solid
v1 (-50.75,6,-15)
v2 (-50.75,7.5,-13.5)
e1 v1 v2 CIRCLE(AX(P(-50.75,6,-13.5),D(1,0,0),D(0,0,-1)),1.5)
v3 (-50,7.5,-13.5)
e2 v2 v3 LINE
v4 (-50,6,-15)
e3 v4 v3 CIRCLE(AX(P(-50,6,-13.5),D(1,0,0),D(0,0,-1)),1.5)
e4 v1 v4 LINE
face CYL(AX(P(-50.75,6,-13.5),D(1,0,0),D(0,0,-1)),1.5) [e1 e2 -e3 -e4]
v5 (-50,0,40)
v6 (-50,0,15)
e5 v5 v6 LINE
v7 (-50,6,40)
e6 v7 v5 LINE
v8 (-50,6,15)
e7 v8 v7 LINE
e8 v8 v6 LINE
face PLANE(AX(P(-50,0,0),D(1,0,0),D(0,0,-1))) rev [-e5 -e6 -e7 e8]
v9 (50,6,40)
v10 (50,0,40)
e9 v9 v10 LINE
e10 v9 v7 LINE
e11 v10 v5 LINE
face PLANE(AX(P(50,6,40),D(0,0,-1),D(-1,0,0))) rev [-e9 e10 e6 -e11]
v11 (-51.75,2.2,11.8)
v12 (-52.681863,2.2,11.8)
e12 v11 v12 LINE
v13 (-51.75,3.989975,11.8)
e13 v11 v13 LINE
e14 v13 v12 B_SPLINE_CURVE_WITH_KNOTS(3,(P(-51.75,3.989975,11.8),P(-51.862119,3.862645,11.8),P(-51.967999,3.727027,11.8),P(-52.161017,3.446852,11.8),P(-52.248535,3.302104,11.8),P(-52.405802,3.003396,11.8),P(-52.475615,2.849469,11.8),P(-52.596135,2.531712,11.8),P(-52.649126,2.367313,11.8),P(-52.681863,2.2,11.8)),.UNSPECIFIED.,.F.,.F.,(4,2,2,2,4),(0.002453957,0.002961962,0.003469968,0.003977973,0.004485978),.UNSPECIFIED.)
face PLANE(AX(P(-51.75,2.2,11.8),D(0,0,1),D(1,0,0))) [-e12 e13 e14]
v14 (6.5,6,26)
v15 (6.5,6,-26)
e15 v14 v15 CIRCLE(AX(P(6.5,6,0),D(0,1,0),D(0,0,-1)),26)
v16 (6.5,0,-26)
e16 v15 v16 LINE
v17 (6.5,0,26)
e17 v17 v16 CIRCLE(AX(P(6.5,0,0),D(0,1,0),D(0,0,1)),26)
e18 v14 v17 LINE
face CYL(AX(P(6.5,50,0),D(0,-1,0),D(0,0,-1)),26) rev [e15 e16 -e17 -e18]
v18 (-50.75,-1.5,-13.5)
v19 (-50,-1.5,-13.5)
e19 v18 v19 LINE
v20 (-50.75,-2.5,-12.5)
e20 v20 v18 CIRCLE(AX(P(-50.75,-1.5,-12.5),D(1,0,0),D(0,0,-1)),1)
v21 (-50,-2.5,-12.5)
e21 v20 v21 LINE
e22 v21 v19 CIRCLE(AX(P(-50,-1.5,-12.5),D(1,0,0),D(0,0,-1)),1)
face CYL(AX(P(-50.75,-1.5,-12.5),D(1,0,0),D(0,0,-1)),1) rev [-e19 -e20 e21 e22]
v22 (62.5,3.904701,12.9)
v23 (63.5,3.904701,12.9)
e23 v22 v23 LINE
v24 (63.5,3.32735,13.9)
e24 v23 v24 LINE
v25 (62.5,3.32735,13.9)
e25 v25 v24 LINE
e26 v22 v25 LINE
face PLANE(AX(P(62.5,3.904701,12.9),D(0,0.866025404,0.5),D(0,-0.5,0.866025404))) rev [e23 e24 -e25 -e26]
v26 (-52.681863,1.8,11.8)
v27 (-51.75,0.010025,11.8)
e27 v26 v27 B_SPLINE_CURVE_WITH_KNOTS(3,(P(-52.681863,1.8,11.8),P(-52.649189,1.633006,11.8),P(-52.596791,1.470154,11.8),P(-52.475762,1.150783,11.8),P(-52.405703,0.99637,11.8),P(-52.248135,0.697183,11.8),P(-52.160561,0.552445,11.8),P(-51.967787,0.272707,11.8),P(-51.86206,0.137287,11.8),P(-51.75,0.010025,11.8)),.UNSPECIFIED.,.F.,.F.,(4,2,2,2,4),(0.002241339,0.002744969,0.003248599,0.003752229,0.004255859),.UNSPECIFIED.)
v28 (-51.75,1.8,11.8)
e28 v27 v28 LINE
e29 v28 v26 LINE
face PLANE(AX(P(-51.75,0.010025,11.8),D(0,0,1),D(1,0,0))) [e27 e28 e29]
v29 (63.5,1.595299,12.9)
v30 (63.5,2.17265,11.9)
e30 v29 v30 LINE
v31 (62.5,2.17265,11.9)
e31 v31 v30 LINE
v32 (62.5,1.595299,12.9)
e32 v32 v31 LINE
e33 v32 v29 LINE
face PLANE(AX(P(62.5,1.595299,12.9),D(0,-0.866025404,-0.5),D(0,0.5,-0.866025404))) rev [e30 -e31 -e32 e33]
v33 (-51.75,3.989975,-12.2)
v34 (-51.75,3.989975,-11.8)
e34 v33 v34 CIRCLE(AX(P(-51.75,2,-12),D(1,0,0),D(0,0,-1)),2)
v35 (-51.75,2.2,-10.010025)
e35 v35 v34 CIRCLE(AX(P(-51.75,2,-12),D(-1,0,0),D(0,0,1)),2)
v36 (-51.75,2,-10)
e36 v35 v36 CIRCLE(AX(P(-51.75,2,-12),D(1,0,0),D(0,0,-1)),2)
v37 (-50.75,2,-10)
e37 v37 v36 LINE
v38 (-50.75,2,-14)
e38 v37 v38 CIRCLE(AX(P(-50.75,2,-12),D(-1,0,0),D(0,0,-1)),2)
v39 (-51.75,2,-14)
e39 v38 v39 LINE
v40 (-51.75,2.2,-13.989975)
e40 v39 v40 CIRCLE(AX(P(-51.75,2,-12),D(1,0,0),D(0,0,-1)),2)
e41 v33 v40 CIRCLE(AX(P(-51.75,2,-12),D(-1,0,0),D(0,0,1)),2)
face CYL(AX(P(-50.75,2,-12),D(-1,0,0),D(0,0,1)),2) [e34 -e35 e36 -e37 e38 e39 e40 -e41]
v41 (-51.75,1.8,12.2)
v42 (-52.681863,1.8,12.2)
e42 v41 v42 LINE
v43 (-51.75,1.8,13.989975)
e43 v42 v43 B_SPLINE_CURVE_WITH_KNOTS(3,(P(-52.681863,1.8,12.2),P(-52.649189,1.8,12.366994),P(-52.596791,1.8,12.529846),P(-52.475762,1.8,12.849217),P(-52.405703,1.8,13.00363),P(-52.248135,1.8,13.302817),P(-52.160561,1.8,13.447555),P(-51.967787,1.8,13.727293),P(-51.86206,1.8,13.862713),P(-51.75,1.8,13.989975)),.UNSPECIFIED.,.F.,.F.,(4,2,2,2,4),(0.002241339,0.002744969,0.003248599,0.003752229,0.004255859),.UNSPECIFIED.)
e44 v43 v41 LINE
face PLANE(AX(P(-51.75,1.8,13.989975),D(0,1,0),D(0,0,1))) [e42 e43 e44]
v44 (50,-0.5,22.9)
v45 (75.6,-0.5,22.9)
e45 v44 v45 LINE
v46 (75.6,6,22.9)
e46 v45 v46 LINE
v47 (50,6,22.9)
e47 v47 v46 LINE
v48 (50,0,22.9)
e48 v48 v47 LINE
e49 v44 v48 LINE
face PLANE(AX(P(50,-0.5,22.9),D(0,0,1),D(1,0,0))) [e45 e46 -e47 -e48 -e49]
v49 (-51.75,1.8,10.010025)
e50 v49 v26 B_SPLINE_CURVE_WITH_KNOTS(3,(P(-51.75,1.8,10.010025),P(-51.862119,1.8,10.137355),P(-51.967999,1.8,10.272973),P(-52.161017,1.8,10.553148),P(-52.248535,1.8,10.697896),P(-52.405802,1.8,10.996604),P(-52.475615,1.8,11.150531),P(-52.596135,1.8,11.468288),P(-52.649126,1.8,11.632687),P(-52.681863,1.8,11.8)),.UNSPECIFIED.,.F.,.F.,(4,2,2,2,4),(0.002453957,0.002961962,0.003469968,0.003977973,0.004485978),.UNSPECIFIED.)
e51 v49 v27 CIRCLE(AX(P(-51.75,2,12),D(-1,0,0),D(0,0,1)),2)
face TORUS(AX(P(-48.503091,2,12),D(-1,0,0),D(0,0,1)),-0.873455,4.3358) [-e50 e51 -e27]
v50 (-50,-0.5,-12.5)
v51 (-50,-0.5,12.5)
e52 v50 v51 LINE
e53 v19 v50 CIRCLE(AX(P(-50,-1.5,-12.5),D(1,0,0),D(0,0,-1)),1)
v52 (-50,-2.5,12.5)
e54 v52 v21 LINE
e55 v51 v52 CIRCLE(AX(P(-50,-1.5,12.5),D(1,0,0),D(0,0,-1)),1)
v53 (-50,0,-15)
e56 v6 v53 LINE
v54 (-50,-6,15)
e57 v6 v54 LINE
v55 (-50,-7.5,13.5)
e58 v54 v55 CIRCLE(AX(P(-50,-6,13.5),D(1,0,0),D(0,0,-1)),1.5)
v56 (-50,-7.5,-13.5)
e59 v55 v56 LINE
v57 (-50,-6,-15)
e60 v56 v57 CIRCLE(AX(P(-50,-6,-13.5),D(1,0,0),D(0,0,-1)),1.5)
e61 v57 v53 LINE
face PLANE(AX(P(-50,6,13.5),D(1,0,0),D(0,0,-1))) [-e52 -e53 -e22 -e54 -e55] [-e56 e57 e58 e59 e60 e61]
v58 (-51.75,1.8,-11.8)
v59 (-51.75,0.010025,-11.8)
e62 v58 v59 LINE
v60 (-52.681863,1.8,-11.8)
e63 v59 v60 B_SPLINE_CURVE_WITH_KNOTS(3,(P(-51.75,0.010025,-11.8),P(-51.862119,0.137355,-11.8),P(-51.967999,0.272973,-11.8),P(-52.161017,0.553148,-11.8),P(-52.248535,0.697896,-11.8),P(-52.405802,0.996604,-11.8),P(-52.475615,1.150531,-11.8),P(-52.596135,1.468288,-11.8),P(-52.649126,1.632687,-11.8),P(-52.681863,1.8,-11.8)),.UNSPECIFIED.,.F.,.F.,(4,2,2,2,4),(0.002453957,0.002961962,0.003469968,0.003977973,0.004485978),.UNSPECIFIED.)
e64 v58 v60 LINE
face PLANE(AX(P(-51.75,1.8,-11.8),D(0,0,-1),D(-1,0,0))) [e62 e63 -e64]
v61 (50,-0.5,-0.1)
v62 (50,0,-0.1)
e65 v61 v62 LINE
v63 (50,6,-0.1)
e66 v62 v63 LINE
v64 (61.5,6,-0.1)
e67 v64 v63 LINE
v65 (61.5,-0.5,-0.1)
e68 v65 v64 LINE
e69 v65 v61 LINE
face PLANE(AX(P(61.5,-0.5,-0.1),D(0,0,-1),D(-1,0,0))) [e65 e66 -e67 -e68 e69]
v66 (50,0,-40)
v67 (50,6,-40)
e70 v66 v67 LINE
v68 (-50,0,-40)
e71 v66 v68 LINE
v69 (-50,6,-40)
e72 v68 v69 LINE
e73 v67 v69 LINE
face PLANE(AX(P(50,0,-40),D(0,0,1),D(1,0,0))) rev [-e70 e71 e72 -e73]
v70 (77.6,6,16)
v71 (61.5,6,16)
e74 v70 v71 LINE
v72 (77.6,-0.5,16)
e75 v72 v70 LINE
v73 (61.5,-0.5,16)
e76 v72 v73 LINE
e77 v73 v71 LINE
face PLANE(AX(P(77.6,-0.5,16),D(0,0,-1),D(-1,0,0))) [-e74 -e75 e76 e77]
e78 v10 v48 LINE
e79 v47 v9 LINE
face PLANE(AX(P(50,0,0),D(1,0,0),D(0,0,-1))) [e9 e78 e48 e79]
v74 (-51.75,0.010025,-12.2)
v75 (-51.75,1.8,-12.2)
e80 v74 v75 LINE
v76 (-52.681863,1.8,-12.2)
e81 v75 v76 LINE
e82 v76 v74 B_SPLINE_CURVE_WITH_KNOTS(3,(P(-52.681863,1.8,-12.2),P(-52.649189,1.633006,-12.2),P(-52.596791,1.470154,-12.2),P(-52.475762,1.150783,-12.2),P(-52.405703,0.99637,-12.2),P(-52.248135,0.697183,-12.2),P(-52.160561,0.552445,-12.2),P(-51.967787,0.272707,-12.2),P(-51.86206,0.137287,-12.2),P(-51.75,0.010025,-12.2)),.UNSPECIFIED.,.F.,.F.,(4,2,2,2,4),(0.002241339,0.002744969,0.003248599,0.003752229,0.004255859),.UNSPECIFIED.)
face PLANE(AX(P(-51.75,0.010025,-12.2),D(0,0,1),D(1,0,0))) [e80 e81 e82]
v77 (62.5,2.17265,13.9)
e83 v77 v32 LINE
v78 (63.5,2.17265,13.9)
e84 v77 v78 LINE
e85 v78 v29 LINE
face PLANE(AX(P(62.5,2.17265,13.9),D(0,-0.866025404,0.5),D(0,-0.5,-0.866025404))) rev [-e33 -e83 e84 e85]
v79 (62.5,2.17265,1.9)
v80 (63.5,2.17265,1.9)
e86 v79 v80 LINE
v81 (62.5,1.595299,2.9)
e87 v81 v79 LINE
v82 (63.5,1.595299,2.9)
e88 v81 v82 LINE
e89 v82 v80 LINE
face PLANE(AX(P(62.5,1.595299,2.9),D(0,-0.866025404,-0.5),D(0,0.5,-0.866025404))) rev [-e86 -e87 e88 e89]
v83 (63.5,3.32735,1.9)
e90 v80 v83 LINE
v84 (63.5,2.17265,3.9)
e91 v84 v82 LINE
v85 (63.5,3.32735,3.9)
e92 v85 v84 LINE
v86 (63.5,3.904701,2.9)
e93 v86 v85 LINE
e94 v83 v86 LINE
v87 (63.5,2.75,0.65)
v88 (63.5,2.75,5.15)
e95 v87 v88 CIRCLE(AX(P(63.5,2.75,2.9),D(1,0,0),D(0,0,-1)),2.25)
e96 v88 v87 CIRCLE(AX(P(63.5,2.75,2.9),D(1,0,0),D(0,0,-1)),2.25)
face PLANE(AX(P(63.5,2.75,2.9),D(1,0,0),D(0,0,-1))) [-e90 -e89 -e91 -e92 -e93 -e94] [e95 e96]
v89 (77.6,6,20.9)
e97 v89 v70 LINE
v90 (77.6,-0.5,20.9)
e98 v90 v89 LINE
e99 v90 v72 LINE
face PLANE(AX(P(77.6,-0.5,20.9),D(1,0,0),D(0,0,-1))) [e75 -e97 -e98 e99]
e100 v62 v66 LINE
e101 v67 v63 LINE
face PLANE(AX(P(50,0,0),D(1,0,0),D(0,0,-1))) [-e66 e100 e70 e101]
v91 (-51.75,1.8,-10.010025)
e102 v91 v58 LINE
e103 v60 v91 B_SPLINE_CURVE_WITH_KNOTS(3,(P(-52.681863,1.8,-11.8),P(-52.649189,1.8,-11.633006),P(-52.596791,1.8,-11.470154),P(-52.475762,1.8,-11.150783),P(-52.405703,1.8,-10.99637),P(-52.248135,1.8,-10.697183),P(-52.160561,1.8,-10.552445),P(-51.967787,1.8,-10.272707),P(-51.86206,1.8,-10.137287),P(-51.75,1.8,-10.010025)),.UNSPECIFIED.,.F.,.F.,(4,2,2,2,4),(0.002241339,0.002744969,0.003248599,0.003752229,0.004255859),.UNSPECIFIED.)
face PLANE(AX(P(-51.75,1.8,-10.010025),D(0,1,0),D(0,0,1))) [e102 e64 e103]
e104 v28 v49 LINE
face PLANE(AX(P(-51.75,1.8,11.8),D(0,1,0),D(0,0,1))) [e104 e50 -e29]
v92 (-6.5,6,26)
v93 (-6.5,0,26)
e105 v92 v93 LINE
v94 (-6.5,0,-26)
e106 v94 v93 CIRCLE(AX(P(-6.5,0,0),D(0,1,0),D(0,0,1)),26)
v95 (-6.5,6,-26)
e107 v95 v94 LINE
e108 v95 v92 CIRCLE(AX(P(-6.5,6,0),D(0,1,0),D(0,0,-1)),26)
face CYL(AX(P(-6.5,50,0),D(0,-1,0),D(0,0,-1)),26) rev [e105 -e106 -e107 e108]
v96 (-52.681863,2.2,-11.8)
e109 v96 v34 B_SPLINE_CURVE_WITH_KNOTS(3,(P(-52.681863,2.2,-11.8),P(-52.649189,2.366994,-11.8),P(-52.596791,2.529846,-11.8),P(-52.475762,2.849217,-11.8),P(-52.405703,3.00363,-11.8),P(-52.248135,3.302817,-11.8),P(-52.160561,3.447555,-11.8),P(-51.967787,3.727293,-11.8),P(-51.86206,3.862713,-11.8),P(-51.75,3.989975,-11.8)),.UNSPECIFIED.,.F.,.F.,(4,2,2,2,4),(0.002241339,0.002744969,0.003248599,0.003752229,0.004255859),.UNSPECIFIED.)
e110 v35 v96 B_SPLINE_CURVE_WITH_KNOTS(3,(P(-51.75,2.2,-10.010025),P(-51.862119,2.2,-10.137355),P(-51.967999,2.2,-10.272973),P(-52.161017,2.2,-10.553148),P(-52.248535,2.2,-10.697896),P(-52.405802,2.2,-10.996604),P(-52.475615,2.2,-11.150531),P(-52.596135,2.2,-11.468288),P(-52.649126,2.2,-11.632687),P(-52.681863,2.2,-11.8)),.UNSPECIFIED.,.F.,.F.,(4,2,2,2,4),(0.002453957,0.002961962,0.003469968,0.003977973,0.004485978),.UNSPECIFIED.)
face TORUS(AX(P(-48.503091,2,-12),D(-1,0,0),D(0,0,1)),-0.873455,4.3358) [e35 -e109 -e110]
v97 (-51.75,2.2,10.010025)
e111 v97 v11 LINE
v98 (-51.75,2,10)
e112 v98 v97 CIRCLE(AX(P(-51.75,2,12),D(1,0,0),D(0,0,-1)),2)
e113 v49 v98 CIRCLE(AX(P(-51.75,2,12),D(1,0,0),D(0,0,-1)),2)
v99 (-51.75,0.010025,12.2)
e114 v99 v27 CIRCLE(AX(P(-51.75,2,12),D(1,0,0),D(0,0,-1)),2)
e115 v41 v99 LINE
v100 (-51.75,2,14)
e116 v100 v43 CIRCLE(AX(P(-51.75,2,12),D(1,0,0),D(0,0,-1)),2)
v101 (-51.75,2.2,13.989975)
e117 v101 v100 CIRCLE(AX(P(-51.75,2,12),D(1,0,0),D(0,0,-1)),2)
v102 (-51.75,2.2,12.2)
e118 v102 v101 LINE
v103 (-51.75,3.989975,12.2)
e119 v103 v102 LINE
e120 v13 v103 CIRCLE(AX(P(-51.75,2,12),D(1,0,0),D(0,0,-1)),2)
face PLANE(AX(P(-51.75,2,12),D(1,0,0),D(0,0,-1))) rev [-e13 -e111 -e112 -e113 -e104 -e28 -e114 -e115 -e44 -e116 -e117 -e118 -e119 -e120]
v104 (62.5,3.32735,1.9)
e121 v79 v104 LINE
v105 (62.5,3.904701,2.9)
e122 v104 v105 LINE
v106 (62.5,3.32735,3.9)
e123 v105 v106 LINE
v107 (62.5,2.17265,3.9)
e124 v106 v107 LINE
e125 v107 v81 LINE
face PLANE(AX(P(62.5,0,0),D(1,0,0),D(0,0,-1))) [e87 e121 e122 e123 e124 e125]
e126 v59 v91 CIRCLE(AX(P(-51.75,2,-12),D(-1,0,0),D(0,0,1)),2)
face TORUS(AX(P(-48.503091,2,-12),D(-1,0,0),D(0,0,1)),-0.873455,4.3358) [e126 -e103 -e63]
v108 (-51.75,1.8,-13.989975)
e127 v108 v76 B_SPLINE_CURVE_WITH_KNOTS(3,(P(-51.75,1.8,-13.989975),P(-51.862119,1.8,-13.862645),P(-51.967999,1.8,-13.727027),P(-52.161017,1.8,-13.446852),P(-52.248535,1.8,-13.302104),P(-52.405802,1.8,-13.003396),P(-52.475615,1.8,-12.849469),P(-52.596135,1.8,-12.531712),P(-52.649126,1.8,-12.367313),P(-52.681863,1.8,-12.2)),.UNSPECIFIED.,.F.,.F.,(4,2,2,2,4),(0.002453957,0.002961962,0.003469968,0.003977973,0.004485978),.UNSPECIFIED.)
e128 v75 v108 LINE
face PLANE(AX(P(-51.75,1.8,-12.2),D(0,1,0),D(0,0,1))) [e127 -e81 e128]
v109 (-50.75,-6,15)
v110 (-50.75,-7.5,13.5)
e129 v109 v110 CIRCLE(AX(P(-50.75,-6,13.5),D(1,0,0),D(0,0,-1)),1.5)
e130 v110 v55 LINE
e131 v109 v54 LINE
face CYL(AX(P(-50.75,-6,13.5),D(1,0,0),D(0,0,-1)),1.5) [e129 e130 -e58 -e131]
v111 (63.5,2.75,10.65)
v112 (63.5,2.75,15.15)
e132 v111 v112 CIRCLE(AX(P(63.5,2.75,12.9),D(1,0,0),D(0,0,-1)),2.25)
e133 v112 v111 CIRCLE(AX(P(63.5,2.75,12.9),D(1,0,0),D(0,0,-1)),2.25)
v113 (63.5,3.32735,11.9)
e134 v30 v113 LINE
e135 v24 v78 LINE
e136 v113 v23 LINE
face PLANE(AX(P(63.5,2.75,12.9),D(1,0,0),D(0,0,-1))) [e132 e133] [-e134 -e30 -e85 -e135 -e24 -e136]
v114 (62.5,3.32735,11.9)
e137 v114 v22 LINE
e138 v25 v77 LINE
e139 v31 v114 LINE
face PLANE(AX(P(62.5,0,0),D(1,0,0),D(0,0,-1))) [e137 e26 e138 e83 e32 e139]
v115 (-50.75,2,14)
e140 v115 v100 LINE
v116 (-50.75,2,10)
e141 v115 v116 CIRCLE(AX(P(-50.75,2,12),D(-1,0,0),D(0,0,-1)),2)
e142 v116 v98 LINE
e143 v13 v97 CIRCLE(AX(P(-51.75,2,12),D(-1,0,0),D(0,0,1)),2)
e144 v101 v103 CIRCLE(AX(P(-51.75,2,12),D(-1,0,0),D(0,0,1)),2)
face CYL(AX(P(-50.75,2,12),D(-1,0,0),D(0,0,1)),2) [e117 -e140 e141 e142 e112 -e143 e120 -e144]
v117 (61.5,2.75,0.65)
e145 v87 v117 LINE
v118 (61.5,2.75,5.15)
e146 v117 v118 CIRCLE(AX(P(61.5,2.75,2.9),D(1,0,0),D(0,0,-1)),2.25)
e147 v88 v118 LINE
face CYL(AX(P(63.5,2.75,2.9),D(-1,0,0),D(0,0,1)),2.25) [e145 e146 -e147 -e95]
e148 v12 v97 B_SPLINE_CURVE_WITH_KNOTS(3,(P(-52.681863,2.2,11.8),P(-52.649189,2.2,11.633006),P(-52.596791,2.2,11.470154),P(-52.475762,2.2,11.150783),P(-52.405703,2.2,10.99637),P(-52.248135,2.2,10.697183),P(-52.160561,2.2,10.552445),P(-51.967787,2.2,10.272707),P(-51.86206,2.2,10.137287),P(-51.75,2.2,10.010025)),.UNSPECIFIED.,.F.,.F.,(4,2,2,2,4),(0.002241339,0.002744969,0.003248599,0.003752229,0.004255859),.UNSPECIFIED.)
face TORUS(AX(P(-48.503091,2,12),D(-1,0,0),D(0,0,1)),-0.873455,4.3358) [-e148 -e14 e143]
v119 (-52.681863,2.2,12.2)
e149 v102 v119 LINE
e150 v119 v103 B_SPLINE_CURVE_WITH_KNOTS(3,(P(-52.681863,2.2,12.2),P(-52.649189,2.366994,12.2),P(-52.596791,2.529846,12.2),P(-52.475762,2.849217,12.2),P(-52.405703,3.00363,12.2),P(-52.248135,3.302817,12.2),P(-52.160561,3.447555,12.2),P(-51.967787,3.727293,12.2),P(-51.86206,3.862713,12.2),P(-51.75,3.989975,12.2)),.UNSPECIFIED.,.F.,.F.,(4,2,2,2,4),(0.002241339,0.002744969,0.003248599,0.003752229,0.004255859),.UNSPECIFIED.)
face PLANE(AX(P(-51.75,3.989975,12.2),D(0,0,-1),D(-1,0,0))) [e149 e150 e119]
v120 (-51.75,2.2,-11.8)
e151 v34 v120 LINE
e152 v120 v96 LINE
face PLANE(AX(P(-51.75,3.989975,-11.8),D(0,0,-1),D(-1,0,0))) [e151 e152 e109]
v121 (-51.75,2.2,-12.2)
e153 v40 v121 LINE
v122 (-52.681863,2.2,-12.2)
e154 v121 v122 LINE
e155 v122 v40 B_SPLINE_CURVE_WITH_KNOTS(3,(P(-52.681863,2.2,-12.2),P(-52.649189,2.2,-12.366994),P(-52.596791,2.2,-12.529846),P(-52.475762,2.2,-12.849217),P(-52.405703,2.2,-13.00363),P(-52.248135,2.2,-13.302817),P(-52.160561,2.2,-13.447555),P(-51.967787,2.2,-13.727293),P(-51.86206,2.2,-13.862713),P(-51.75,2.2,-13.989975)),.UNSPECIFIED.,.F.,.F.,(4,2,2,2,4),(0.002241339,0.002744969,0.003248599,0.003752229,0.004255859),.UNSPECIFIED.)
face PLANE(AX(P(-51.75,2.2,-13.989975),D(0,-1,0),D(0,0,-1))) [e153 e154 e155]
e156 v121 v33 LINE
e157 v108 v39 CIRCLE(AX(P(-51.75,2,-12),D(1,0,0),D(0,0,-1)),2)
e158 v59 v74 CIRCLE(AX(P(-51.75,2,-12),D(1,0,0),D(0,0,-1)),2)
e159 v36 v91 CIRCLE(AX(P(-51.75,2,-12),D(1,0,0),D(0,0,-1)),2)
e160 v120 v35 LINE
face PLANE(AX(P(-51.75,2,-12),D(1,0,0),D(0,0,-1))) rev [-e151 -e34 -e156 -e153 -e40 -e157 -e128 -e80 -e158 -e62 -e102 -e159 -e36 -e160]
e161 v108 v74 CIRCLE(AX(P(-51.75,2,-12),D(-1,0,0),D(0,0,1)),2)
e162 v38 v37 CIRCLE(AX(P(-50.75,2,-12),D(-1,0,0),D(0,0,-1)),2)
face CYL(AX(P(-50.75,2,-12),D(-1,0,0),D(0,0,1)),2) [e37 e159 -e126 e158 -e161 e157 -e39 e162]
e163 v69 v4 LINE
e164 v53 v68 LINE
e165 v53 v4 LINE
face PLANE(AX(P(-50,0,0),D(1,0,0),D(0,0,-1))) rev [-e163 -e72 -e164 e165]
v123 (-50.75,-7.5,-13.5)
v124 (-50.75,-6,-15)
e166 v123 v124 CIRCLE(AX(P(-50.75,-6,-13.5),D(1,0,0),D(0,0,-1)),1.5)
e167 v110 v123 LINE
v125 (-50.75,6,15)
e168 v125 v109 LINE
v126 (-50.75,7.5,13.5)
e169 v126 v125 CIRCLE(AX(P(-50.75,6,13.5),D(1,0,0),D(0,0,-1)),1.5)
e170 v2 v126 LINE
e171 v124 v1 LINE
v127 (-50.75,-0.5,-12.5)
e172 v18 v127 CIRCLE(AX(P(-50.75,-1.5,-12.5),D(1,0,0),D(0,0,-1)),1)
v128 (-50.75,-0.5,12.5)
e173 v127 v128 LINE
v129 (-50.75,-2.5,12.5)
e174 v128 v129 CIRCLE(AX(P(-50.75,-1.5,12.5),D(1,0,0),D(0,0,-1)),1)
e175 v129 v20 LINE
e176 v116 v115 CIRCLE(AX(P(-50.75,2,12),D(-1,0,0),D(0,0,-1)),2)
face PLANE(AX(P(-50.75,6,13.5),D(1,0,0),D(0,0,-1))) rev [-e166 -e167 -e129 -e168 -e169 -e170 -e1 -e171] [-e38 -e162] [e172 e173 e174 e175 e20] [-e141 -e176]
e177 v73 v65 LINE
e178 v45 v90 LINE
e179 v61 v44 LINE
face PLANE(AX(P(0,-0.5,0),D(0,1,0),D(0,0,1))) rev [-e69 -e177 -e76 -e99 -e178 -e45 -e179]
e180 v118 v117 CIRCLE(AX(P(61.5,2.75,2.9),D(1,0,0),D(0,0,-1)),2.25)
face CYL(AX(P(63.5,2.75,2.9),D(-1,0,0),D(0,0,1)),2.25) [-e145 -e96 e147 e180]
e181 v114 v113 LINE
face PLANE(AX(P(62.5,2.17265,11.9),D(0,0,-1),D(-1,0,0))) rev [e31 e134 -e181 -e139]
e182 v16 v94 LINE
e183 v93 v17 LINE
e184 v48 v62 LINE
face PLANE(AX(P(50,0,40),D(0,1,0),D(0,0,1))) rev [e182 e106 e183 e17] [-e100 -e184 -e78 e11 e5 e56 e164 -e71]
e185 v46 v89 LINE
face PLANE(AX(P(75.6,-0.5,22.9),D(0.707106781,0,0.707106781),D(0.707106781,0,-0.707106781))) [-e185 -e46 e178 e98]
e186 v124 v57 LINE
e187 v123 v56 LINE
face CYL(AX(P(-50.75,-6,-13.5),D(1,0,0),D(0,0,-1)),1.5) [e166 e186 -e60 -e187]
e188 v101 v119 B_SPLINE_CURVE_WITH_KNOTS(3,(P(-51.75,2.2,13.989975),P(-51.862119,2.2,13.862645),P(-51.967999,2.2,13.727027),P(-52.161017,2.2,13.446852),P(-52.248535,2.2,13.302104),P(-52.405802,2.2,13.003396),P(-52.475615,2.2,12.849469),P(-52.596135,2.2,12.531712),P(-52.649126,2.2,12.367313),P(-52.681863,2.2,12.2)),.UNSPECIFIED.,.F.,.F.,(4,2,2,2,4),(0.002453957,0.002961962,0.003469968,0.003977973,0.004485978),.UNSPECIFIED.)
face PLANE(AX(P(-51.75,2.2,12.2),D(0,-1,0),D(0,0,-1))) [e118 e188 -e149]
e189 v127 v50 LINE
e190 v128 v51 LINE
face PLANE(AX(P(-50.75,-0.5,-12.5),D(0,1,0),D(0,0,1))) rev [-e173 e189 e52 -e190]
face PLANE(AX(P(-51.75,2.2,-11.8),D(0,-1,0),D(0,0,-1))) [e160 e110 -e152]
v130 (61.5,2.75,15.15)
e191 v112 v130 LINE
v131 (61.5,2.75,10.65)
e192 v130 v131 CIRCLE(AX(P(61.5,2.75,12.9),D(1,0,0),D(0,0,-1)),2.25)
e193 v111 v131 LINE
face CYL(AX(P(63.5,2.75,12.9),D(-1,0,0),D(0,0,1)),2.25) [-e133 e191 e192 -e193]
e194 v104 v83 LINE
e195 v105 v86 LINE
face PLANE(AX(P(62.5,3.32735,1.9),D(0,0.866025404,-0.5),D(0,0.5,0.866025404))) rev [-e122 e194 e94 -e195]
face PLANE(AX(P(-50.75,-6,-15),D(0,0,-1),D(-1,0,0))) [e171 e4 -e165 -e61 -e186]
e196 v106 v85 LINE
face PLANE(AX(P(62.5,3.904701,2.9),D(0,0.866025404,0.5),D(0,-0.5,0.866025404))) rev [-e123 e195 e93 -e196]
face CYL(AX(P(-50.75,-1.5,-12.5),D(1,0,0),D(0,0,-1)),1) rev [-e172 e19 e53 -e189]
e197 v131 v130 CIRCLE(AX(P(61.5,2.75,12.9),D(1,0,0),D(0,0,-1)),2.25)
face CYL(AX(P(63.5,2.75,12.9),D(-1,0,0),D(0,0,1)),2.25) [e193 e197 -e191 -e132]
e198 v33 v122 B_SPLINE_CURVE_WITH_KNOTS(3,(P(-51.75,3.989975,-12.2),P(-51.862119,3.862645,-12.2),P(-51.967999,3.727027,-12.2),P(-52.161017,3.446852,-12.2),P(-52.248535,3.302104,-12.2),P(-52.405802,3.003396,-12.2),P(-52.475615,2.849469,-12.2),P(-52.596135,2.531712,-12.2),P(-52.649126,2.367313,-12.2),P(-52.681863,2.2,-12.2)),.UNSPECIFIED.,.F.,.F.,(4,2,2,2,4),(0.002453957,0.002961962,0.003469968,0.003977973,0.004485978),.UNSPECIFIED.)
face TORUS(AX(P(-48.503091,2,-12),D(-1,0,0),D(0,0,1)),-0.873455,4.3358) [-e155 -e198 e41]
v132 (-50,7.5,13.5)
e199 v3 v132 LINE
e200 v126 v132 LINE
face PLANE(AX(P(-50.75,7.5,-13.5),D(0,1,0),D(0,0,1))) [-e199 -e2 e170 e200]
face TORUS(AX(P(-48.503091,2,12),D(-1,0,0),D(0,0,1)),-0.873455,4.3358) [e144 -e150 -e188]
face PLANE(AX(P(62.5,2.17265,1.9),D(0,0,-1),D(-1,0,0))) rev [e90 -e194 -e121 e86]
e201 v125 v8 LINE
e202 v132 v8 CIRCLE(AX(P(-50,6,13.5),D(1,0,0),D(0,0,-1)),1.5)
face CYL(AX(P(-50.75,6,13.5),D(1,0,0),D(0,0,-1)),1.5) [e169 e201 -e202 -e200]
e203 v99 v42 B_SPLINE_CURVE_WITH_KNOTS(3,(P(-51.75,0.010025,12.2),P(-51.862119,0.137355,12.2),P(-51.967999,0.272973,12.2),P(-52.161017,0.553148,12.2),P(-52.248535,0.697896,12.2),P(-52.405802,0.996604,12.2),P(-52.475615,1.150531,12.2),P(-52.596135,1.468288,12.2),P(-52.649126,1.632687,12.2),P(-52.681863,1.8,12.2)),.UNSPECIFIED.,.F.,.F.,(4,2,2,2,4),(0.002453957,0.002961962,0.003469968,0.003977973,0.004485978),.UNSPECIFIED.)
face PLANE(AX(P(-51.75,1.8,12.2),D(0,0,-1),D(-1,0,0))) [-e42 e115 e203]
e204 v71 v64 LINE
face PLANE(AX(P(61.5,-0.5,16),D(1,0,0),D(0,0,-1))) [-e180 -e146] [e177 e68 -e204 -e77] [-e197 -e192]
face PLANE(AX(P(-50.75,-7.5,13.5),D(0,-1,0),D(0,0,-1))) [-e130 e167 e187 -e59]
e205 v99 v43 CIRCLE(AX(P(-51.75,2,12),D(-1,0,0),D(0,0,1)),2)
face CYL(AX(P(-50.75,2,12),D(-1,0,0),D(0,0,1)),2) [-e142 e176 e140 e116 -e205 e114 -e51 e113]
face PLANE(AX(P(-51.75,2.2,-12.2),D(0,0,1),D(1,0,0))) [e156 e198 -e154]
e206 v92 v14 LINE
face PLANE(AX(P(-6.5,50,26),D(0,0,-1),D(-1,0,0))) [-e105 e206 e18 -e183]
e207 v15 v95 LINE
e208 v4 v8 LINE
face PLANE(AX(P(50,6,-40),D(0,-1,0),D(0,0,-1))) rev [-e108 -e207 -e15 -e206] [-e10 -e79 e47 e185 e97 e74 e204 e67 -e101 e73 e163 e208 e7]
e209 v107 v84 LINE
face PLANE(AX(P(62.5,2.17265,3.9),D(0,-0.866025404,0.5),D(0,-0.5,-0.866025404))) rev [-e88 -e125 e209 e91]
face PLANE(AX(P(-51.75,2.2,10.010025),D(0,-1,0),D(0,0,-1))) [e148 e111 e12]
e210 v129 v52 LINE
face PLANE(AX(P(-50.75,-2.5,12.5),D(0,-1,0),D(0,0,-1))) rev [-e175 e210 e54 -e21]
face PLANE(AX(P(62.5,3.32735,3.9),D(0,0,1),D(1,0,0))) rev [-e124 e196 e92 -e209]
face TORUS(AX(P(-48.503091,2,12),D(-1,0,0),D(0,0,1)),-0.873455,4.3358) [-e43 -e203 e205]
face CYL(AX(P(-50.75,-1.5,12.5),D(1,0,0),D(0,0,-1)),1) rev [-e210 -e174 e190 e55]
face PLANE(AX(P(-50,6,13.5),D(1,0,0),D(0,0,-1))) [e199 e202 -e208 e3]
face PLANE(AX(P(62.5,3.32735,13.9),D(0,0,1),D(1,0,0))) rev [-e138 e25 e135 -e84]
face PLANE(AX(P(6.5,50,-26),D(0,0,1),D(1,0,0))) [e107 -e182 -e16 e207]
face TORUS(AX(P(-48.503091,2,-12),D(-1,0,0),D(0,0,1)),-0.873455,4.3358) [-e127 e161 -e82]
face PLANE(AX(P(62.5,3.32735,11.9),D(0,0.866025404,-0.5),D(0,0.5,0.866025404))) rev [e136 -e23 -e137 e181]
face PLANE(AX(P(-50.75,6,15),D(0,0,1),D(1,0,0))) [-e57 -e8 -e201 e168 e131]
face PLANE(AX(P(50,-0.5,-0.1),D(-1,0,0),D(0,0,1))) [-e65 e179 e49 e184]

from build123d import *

# Parameters (mm, degrees)
EXTRUDE_1_DEPTH      = 50
EXTRUDE_1_DEPTH_BACK = 50
SKETCH_1_W           = 80
SKETCH_1_H           = 6
EXTRUDE_2_DEPTH      = 6.5
EXTRUDE_3_DEPTH      = 0.75
CUT_EXTRUDE_START    = 1
CUT_EXTRUDE_1_DEPTH  = 1
CUT_EXTRUDE_2_DEPTH  = 1
CUT_EXTRUDE_3_DEPTH  = 50
SKETCH_9_R           = 2.25
EXTRUDE_4_DEPTH      = 2
SKETCH_10_R          = 2.25
EXTRUDE_5_DEPTH      = 2
CUT_EXTRUDE_4_DEPTH  = 1
CUT_EXTRUDE_5_DEPTH  = 1


with BuildPart() as part:
    # 草图1 → 凸台-拉伸1 (new, two sides: drawn at the far end of the back side and taken through both)
    with BuildSketch(Plane(origin=(0, 0, 0), x_dir=(0, 0, -1), z_dir=(1, 0, 0)).offset(-EXTRUDE_1_DEPTH_BACK)):
        with Locations((0, 3)):
            Rectangle(SKETCH_1_W, SKETCH_1_H)
    extrude(amount=EXTRUDE_1_DEPTH + EXTRUDE_1_DEPTH_BACK)

    # 草图2 → 凸台-拉伸2 (add)
    with BuildSketch(Plane(origin=(0, 6, 0), x_dir=(-1, 0, 0), z_dir=(0, 1, 0))):
        Polygon((-50, -0.1), (-50, 22.9), (-75.6, 22.9), (-77.6, 20.9), (-77.6, 16), (-61.5, 16), (-61.5, -0.1), align=None)
    extrude(amount=-EXTRUDE_2_DEPTH)

    # 草图3 → 凸台-拉伸3 (add)
    with BuildSketch(Plane(origin=(-50, 0, 0), x_dir=(0, 0, -1), z_dir=(1, 0, 0))):
        with BuildLine():
            Line((-15, 6), (-15, -6))
            ThreePointArc((-15, -6), (-14.560660172, -7.060660172), (-13.5, -7.5))
            Line((-13.5, -7.5), (13.5, -7.5))
            ThreePointArc((13.5, -7.5), (14.560660172, -7.060660172), (15, -6))
            Line((15, -6), (15, 6))
            ThreePointArc((15, 6), (14.560660172, 7.060660172), (13.5, 7.5))
            Line((13.5, 7.5), (-13.5, 7.5))
            ThreePointArc((-13.5, 7.5), (-14.560660172, 7.060660172), (-15, 6))
        make_face()
        with BuildLine():
            Line((-12.5, -2.5), (12.5, -2.5))
            ThreePointArc((12.5, -2.5), (13.5, -1.5), (12.5, -0.5))
            Line((12.5, -0.5), (-12.5, -0.5))
            ThreePointArc((-12.5, -0.5), (-13.5, -1.5), (-12.5, -2.5))
        make_face(mode=Mode.SUBTRACT)
    extrude(amount=-EXTRUDE_3_DEPTH)

    # 草图4 → 旋转1 (revolve)
    with BuildSketch(Plane.XY.offset(-12), mode=Mode.PRIVATE) as revolve_1_sk:
        with BuildLine():
            Line((-51.75, 4), (-50.75, 4))
            Line((-50.75, 4), (-50.75, 2))
            Line((-50.75, 2), (-52.75, 2))
            ThreePointArc((-52.75, 2), (-52.381148113, 3.065574057), (-51.75, 4))
        make_face()
    revolve(revolve_1_sk.sketch.rotate(Axis((-50.75, 2, -12), (-1, 0, 0)), 270), axis=Axis((-50.75, 2, -12), (-1, 0, 0)))

    # 草图5 → 旋转2 (revolve)
    with BuildSketch(Plane.XY.offset(12), mode=Mode.PRIVATE) as revolve_2_sk:
        with BuildLine():
            Line((-51.75, 4), (-50.75, 4))
            Line((-50.75, 4), (-50.75, 2))
            Line((-50.75, 2), (-52.75, 2))
            ThreePointArc((-52.75, 2), (-52.381148113, 3.065574057), (-51.75, 4))
        make_face()
    revolve(revolve_2_sk.sketch.rotate(Axis((-50.75, 2, 12), (-1, 0, 0)), 270), axis=Axis((-50.75, 2, 12), (-1, 0, 0)))

    # 草图6 → 切除-拉伸1 (cut)
    with BuildSketch(Plane(origin=(-52.75, 0, 0), x_dir=(0, 0, -1), z_dir=(1, 0, 0)).offset(CUT_EXTRUDE_START)):
        with BuildLine():
            Line((-13.989974874, 1.8), (-12.2, 1.8))
            Line((-12.2, 1.8), (-12.2, 0.010025126))
            ThreePointArc((-12.2, 0.010025126), (-12, 0), (-11.8, 0.010025126))
            Line((-11.8, 0.010025126), (-11.8, 1.8))
            Line((-11.8, 1.8), (-10.010025126, 1.8))
            ThreePointArc((-10.010025126, 1.8), (-10, 2), (-10.010025126, 2.2))
            Line((-10.010025126, 2.2), (-11.8, 2.2))
            Line((-11.8, 2.2), (-11.8, 3.989974874))
            ThreePointArc((-11.8, 3.989974874), (-12, 4), (-12.2, 3.989974874))
            Line((-12.2, 3.989974874), (-12.2, 2.2))
            Line((-12.2, 2.2), (-13.989974874, 2.2))
            ThreePointArc((-13.989974874, 2.2), (-14, 2), (-13.989974874, 1.8))
        make_face()
    extrude(amount=-CUT_EXTRUDE_1_DEPTH, mode=Mode.SUBTRACT)

    # 草图7 → 切除-拉伸2 (cut)
    with BuildSketch(Plane(origin=(-52.75, 0, 0), x_dir=(0, 0, -1), z_dir=(1, 0, 0)).offset(CUT_EXTRUDE_START)):
        with BuildLine():
            Line((10.010025126, 1.8), (11.8, 1.8))
            Line((11.8, 1.8), (11.8, 0.010025126))
            ThreePointArc((11.8, 0.010025126), (12, 0), (12.2, 0.010025126))
            Line((12.2, 0.010025126), (12.2, 1.8))
            Line((12.2, 1.8), (13.989974874, 1.8))
            ThreePointArc((13.989974874, 1.8), (14, 2), (13.989974874, 2.2))
            Line((13.989974874, 2.2), (12.2, 2.2))
            Line((12.2, 2.2), (12.2, 3.989974874))
            ThreePointArc((12.2, 3.989974874), (12, 4), (11.8, 3.989974874))
            Line((11.8, 3.989974874), (11.8, 2.2))
            Line((11.8, 2.2), (10.010025126, 2.2))
            ThreePointArc((10.010025126, 2.2), (10, 2), (10.010025126, 1.8))
        make_face()
    extrude(amount=-CUT_EXTRUDE_2_DEPTH, mode=Mode.SUBTRACT)

    # 草图8 → 切除-拉伸3 (cut)
    with BuildSketch(Plane(origin=(0, 0, 0), x_dir=(-1, 0, 0), z_dir=(0, 1, 0))):
        with BuildLine():
            Line((6.5, 26), (-6.5, 26))
            ThreePointArc((-6.5, 26), (-32.5, 0), (-6.5, -26))
            Line((-6.5, -26), (6.5, -26))
            ThreePointArc((6.5, -26), (32.5, 0), (6.5, 26))
        make_face()
    extrude(amount=CUT_EXTRUDE_3_DEPTH, mode=Mode.SUBTRACT)

    # 草图9 → 凸台-拉伸4 (add)
    with BuildSketch(Plane(origin=(61.5, 0, 0), x_dir=(0, 0, -1), z_dir=(1, 0, 0))):
        with Locations((-2.9, 2.75)):
            Circle(SKETCH_9_R)
    extrude(amount=EXTRUDE_4_DEPTH)

    # 草图10 → 凸台-拉伸5 (add)
    with BuildSketch(Plane(origin=(61.5, 0, 0), x_dir=(0, 0, -1), z_dir=(1, 0, 0))):
        with Locations((-12.9, 2.75)):
            Circle(SKETCH_10_R)
    extrude(amount=EXTRUDE_5_DEPTH)

    # 草图11 → 切除-拉伸4 (cut)
    with BuildSketch(Plane(origin=(63.5, 0, 0), x_dir=(0, 0, -1), z_dir=(1, 0, 0))):
        Polygon((-1.9, 3.327350269), (-2.9, 3.904700538), (-3.9, 3.327350269), (-3.9, 2.172649731), (-2.9, 1.595299462), (-1.9, 2.172649731), align=None)
    extrude(amount=-CUT_EXTRUDE_4_DEPTH, mode=Mode.SUBTRACT)

    # 草图12 → 切除-拉伸5 (cut)
    with BuildSketch(Plane(origin=(63.5, 0, 0), x_dir=(0, 0, -1), z_dir=(1, 0, 0))):
        Polygon((-11.9, 3.327350269), (-12.9, 3.904700538), (-13.9, 3.327350269), (-13.9, 2.172649731), (-12.9, 1.595299462), (-11.9, 2.172649731), align=None)
    extrude(amount=-CUT_EXTRUDE_5_DEPTH, mode=Mode.SUBTRACT)


solid = part.part
